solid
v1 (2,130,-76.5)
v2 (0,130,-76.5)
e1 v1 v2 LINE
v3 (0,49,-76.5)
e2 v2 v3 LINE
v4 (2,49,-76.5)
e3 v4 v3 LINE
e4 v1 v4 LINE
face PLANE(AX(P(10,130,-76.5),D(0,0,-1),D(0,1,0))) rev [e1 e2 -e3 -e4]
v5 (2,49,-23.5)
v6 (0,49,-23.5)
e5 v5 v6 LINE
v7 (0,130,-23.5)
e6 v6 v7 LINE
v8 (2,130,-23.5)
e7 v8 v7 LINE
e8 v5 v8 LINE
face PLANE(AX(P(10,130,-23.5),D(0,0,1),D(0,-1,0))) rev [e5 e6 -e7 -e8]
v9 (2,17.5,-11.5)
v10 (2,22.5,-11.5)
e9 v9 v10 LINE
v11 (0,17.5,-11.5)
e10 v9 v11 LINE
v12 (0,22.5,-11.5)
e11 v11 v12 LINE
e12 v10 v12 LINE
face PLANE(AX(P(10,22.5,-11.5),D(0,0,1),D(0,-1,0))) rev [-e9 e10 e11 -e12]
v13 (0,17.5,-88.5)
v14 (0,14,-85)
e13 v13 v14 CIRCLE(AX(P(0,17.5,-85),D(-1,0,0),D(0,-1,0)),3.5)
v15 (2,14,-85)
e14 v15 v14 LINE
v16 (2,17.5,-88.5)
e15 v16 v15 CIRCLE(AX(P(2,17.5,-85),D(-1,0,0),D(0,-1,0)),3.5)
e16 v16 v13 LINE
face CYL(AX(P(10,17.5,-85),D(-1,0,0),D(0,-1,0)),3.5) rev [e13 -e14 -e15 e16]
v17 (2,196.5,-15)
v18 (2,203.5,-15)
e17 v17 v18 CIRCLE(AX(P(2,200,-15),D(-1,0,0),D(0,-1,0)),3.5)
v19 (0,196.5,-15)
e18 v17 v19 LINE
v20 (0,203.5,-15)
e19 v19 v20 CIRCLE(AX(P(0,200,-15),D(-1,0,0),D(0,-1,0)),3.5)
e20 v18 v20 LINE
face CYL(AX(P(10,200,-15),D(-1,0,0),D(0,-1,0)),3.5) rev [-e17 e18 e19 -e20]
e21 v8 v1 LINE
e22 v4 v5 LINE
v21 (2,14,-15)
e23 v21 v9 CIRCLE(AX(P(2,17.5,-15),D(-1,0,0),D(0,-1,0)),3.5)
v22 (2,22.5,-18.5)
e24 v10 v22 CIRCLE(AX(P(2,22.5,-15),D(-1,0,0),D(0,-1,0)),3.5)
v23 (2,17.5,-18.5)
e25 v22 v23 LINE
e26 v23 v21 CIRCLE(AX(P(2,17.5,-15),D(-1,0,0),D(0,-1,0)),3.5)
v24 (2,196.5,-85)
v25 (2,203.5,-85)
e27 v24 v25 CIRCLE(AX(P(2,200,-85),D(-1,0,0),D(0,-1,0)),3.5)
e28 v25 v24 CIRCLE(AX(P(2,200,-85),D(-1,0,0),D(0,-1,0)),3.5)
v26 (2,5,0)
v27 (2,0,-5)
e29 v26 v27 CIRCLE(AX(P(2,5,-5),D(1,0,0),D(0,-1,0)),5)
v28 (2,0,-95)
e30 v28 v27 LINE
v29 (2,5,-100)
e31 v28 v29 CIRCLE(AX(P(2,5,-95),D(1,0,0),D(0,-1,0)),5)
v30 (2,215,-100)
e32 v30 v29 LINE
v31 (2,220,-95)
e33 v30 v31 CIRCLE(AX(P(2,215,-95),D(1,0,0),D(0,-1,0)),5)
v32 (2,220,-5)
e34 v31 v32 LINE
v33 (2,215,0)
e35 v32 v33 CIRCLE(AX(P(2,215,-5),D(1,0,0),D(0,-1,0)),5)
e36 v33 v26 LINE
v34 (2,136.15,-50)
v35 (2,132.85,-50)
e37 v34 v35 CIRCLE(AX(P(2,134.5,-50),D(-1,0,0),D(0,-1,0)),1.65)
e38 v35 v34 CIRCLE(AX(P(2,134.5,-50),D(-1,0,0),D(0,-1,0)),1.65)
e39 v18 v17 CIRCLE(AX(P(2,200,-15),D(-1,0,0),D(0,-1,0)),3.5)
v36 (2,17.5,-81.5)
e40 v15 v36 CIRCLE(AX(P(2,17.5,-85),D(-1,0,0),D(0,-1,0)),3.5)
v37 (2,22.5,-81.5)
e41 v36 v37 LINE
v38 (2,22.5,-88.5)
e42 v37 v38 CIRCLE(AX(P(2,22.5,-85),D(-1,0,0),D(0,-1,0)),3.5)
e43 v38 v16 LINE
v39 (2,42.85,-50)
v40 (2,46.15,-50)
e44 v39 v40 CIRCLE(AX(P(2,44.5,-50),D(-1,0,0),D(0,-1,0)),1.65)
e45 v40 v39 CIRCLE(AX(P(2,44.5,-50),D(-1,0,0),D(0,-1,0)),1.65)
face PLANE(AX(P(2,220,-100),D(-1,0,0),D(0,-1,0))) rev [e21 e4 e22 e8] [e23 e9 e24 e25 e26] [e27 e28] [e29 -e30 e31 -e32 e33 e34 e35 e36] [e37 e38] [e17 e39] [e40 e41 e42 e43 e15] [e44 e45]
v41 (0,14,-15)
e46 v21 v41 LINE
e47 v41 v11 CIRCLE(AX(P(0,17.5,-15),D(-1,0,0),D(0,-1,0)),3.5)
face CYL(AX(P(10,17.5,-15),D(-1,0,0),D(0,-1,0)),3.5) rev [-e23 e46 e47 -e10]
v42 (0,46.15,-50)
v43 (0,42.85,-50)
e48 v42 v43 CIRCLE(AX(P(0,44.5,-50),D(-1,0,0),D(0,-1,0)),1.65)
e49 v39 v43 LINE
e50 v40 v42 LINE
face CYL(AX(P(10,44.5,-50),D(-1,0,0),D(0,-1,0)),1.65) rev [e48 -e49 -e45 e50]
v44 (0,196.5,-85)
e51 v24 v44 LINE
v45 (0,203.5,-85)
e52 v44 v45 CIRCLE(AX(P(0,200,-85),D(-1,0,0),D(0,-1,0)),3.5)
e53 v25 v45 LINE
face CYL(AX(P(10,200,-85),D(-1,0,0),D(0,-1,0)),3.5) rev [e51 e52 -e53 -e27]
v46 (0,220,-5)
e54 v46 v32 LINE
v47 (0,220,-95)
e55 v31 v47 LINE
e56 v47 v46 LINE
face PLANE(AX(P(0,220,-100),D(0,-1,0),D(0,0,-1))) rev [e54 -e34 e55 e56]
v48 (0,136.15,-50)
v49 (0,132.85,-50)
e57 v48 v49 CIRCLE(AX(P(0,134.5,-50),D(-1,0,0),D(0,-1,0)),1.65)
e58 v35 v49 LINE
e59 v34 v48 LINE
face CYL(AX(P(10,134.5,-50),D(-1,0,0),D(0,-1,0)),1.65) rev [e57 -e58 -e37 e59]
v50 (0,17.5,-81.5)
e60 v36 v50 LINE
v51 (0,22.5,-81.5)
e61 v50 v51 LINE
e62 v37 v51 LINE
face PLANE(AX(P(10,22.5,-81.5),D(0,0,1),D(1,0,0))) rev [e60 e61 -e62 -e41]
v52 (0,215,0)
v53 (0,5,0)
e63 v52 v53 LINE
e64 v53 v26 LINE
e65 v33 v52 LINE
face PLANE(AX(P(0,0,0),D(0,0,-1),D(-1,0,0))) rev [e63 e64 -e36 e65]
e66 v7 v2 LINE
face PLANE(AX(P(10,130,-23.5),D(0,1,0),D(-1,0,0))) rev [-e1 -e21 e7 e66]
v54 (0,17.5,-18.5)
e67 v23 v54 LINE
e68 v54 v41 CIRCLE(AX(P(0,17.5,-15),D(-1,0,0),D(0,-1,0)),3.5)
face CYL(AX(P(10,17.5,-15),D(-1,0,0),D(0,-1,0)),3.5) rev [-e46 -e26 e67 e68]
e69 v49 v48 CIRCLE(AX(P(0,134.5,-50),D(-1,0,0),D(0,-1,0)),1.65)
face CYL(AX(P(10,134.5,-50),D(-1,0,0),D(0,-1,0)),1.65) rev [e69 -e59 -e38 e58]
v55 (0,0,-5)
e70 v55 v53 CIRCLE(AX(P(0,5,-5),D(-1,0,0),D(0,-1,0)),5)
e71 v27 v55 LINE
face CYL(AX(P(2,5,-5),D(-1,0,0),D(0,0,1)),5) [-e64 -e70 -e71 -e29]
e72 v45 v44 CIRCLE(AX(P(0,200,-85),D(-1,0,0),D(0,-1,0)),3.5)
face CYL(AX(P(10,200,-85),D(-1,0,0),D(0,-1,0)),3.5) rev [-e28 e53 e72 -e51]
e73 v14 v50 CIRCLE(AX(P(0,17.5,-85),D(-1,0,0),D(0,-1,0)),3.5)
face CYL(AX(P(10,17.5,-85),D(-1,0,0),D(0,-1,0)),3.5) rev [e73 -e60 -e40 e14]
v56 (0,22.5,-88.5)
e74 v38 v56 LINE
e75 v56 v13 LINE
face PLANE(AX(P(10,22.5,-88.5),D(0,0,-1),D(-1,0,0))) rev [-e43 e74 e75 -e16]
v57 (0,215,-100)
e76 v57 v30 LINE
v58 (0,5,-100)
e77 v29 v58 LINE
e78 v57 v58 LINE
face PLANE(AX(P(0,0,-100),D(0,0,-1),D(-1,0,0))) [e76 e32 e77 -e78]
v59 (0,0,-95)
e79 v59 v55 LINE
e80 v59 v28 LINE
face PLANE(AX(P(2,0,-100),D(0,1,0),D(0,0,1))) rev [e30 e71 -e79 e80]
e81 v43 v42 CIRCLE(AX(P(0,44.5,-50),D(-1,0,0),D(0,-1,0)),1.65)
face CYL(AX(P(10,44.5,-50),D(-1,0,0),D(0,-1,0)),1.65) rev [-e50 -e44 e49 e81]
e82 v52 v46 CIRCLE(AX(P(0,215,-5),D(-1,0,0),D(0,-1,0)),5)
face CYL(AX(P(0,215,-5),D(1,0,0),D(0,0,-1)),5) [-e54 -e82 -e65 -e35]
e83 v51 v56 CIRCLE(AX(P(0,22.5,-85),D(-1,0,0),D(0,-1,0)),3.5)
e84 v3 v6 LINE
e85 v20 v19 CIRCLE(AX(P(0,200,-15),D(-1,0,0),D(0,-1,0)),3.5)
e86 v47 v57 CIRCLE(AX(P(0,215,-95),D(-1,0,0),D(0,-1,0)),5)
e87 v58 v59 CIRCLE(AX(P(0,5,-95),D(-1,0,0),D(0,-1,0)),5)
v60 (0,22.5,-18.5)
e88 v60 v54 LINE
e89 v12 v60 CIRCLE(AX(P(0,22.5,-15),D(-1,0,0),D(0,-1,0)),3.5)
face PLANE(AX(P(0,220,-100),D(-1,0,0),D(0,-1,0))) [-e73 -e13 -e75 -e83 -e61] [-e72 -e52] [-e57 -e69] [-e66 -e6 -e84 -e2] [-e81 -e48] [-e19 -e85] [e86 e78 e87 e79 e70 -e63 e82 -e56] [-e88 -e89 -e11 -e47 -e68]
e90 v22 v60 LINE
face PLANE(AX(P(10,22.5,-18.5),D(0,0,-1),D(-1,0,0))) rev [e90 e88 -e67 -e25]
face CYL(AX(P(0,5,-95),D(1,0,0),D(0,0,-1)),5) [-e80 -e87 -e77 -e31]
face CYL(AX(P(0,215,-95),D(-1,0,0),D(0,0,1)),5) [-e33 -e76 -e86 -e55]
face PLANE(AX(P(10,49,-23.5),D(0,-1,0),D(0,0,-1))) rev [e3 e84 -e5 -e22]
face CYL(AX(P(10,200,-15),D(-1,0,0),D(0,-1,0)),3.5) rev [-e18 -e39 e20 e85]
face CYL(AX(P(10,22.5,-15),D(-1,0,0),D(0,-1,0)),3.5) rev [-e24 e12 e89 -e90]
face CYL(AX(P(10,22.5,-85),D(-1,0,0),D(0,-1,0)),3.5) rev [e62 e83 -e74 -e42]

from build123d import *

# Parameters (mm, degrees)
SKETCH_1_W          = 2
SKETCH_1_H          = 220
EXTRUDE_1_DEPTH     = 100
SKETCH_2_R          = 1.65
SKETCH_2_R_2        = 3.5
SKETCH_2_W          = 53
SKETCH_2_H          = 81
CUT_EXTRUDE_1_DEPTH = 10
FILLET_1_R          = 5


with BuildPart() as part:
    # 草图1 → 拉伸-薄壁1 (new body)
    with BuildSketch(Plane.XY):
        with Locations((1, 110)):
            Rectangle(SKETCH_1_W, SKETCH_1_H)
    extrude(amount=-EXTRUDE_1_DEPTH)

    # 草图2 → 切除-拉伸1 (cut)
    with BuildSketch(Plane.ZY):
        with Locations(Location((-50, 44.5, 0), (0, 0, 270))):
            Circle(SKETCH_2_R)
        with Locations(Location((-50, 134.5, 0), (0, 0, 270))):
            Circle(SKETCH_2_R)
        with Locations(Location((-15, 200, 0), (0, 0, 270))):
            Circle(SKETCH_2_R_2)
        with Locations(Location((-85, 200, 0), (0, 0, 270))):
            Circle(SKETCH_2_R_2)
        with Locations((-50, 89.5)):
            Rectangle(SKETCH_2_W, SKETCH_2_H)
        with BuildLine():
            Line((-11.5, 22.5), (-11.5, 17.5))
            ThreePointArc((-11.5, 17.5), (-15, 14), (-18.5, 17.5))
            Line((-18.5, 17.5), (-18.5, 22.5))
            ThreePointArc((-18.5, 22.5), (-15, 26), (-11.5, 22.5))
        make_face()
        with BuildLine():
            Line((-81.5, 22.5), (-81.5, 17.5))
            ThreePointArc((-81.5, 17.5), (-85, 14), (-88.5, 17.5))
            Line((-88.5, 17.5), (-88.5, 22.5))
            ThreePointArc((-88.5, 22.5), (-85, 26), (-81.5, 22.5))
        make_face()
    extrude(amount=-CUT_EXTRUDE_1_DEPTH, mode=Mode.SUBTRACT)

    # 圆角1
    fillet_1_edges = [part.edges().sort_by_distance(p)[0] for p in [
        (1, 220, -100),
        (1, 220, 0),
        (1, 0, 0),
        (1, 0, -100),
    ]]
    fillet(fillet_1_edges, radius=FILLET_1_R)


solid = part.part
